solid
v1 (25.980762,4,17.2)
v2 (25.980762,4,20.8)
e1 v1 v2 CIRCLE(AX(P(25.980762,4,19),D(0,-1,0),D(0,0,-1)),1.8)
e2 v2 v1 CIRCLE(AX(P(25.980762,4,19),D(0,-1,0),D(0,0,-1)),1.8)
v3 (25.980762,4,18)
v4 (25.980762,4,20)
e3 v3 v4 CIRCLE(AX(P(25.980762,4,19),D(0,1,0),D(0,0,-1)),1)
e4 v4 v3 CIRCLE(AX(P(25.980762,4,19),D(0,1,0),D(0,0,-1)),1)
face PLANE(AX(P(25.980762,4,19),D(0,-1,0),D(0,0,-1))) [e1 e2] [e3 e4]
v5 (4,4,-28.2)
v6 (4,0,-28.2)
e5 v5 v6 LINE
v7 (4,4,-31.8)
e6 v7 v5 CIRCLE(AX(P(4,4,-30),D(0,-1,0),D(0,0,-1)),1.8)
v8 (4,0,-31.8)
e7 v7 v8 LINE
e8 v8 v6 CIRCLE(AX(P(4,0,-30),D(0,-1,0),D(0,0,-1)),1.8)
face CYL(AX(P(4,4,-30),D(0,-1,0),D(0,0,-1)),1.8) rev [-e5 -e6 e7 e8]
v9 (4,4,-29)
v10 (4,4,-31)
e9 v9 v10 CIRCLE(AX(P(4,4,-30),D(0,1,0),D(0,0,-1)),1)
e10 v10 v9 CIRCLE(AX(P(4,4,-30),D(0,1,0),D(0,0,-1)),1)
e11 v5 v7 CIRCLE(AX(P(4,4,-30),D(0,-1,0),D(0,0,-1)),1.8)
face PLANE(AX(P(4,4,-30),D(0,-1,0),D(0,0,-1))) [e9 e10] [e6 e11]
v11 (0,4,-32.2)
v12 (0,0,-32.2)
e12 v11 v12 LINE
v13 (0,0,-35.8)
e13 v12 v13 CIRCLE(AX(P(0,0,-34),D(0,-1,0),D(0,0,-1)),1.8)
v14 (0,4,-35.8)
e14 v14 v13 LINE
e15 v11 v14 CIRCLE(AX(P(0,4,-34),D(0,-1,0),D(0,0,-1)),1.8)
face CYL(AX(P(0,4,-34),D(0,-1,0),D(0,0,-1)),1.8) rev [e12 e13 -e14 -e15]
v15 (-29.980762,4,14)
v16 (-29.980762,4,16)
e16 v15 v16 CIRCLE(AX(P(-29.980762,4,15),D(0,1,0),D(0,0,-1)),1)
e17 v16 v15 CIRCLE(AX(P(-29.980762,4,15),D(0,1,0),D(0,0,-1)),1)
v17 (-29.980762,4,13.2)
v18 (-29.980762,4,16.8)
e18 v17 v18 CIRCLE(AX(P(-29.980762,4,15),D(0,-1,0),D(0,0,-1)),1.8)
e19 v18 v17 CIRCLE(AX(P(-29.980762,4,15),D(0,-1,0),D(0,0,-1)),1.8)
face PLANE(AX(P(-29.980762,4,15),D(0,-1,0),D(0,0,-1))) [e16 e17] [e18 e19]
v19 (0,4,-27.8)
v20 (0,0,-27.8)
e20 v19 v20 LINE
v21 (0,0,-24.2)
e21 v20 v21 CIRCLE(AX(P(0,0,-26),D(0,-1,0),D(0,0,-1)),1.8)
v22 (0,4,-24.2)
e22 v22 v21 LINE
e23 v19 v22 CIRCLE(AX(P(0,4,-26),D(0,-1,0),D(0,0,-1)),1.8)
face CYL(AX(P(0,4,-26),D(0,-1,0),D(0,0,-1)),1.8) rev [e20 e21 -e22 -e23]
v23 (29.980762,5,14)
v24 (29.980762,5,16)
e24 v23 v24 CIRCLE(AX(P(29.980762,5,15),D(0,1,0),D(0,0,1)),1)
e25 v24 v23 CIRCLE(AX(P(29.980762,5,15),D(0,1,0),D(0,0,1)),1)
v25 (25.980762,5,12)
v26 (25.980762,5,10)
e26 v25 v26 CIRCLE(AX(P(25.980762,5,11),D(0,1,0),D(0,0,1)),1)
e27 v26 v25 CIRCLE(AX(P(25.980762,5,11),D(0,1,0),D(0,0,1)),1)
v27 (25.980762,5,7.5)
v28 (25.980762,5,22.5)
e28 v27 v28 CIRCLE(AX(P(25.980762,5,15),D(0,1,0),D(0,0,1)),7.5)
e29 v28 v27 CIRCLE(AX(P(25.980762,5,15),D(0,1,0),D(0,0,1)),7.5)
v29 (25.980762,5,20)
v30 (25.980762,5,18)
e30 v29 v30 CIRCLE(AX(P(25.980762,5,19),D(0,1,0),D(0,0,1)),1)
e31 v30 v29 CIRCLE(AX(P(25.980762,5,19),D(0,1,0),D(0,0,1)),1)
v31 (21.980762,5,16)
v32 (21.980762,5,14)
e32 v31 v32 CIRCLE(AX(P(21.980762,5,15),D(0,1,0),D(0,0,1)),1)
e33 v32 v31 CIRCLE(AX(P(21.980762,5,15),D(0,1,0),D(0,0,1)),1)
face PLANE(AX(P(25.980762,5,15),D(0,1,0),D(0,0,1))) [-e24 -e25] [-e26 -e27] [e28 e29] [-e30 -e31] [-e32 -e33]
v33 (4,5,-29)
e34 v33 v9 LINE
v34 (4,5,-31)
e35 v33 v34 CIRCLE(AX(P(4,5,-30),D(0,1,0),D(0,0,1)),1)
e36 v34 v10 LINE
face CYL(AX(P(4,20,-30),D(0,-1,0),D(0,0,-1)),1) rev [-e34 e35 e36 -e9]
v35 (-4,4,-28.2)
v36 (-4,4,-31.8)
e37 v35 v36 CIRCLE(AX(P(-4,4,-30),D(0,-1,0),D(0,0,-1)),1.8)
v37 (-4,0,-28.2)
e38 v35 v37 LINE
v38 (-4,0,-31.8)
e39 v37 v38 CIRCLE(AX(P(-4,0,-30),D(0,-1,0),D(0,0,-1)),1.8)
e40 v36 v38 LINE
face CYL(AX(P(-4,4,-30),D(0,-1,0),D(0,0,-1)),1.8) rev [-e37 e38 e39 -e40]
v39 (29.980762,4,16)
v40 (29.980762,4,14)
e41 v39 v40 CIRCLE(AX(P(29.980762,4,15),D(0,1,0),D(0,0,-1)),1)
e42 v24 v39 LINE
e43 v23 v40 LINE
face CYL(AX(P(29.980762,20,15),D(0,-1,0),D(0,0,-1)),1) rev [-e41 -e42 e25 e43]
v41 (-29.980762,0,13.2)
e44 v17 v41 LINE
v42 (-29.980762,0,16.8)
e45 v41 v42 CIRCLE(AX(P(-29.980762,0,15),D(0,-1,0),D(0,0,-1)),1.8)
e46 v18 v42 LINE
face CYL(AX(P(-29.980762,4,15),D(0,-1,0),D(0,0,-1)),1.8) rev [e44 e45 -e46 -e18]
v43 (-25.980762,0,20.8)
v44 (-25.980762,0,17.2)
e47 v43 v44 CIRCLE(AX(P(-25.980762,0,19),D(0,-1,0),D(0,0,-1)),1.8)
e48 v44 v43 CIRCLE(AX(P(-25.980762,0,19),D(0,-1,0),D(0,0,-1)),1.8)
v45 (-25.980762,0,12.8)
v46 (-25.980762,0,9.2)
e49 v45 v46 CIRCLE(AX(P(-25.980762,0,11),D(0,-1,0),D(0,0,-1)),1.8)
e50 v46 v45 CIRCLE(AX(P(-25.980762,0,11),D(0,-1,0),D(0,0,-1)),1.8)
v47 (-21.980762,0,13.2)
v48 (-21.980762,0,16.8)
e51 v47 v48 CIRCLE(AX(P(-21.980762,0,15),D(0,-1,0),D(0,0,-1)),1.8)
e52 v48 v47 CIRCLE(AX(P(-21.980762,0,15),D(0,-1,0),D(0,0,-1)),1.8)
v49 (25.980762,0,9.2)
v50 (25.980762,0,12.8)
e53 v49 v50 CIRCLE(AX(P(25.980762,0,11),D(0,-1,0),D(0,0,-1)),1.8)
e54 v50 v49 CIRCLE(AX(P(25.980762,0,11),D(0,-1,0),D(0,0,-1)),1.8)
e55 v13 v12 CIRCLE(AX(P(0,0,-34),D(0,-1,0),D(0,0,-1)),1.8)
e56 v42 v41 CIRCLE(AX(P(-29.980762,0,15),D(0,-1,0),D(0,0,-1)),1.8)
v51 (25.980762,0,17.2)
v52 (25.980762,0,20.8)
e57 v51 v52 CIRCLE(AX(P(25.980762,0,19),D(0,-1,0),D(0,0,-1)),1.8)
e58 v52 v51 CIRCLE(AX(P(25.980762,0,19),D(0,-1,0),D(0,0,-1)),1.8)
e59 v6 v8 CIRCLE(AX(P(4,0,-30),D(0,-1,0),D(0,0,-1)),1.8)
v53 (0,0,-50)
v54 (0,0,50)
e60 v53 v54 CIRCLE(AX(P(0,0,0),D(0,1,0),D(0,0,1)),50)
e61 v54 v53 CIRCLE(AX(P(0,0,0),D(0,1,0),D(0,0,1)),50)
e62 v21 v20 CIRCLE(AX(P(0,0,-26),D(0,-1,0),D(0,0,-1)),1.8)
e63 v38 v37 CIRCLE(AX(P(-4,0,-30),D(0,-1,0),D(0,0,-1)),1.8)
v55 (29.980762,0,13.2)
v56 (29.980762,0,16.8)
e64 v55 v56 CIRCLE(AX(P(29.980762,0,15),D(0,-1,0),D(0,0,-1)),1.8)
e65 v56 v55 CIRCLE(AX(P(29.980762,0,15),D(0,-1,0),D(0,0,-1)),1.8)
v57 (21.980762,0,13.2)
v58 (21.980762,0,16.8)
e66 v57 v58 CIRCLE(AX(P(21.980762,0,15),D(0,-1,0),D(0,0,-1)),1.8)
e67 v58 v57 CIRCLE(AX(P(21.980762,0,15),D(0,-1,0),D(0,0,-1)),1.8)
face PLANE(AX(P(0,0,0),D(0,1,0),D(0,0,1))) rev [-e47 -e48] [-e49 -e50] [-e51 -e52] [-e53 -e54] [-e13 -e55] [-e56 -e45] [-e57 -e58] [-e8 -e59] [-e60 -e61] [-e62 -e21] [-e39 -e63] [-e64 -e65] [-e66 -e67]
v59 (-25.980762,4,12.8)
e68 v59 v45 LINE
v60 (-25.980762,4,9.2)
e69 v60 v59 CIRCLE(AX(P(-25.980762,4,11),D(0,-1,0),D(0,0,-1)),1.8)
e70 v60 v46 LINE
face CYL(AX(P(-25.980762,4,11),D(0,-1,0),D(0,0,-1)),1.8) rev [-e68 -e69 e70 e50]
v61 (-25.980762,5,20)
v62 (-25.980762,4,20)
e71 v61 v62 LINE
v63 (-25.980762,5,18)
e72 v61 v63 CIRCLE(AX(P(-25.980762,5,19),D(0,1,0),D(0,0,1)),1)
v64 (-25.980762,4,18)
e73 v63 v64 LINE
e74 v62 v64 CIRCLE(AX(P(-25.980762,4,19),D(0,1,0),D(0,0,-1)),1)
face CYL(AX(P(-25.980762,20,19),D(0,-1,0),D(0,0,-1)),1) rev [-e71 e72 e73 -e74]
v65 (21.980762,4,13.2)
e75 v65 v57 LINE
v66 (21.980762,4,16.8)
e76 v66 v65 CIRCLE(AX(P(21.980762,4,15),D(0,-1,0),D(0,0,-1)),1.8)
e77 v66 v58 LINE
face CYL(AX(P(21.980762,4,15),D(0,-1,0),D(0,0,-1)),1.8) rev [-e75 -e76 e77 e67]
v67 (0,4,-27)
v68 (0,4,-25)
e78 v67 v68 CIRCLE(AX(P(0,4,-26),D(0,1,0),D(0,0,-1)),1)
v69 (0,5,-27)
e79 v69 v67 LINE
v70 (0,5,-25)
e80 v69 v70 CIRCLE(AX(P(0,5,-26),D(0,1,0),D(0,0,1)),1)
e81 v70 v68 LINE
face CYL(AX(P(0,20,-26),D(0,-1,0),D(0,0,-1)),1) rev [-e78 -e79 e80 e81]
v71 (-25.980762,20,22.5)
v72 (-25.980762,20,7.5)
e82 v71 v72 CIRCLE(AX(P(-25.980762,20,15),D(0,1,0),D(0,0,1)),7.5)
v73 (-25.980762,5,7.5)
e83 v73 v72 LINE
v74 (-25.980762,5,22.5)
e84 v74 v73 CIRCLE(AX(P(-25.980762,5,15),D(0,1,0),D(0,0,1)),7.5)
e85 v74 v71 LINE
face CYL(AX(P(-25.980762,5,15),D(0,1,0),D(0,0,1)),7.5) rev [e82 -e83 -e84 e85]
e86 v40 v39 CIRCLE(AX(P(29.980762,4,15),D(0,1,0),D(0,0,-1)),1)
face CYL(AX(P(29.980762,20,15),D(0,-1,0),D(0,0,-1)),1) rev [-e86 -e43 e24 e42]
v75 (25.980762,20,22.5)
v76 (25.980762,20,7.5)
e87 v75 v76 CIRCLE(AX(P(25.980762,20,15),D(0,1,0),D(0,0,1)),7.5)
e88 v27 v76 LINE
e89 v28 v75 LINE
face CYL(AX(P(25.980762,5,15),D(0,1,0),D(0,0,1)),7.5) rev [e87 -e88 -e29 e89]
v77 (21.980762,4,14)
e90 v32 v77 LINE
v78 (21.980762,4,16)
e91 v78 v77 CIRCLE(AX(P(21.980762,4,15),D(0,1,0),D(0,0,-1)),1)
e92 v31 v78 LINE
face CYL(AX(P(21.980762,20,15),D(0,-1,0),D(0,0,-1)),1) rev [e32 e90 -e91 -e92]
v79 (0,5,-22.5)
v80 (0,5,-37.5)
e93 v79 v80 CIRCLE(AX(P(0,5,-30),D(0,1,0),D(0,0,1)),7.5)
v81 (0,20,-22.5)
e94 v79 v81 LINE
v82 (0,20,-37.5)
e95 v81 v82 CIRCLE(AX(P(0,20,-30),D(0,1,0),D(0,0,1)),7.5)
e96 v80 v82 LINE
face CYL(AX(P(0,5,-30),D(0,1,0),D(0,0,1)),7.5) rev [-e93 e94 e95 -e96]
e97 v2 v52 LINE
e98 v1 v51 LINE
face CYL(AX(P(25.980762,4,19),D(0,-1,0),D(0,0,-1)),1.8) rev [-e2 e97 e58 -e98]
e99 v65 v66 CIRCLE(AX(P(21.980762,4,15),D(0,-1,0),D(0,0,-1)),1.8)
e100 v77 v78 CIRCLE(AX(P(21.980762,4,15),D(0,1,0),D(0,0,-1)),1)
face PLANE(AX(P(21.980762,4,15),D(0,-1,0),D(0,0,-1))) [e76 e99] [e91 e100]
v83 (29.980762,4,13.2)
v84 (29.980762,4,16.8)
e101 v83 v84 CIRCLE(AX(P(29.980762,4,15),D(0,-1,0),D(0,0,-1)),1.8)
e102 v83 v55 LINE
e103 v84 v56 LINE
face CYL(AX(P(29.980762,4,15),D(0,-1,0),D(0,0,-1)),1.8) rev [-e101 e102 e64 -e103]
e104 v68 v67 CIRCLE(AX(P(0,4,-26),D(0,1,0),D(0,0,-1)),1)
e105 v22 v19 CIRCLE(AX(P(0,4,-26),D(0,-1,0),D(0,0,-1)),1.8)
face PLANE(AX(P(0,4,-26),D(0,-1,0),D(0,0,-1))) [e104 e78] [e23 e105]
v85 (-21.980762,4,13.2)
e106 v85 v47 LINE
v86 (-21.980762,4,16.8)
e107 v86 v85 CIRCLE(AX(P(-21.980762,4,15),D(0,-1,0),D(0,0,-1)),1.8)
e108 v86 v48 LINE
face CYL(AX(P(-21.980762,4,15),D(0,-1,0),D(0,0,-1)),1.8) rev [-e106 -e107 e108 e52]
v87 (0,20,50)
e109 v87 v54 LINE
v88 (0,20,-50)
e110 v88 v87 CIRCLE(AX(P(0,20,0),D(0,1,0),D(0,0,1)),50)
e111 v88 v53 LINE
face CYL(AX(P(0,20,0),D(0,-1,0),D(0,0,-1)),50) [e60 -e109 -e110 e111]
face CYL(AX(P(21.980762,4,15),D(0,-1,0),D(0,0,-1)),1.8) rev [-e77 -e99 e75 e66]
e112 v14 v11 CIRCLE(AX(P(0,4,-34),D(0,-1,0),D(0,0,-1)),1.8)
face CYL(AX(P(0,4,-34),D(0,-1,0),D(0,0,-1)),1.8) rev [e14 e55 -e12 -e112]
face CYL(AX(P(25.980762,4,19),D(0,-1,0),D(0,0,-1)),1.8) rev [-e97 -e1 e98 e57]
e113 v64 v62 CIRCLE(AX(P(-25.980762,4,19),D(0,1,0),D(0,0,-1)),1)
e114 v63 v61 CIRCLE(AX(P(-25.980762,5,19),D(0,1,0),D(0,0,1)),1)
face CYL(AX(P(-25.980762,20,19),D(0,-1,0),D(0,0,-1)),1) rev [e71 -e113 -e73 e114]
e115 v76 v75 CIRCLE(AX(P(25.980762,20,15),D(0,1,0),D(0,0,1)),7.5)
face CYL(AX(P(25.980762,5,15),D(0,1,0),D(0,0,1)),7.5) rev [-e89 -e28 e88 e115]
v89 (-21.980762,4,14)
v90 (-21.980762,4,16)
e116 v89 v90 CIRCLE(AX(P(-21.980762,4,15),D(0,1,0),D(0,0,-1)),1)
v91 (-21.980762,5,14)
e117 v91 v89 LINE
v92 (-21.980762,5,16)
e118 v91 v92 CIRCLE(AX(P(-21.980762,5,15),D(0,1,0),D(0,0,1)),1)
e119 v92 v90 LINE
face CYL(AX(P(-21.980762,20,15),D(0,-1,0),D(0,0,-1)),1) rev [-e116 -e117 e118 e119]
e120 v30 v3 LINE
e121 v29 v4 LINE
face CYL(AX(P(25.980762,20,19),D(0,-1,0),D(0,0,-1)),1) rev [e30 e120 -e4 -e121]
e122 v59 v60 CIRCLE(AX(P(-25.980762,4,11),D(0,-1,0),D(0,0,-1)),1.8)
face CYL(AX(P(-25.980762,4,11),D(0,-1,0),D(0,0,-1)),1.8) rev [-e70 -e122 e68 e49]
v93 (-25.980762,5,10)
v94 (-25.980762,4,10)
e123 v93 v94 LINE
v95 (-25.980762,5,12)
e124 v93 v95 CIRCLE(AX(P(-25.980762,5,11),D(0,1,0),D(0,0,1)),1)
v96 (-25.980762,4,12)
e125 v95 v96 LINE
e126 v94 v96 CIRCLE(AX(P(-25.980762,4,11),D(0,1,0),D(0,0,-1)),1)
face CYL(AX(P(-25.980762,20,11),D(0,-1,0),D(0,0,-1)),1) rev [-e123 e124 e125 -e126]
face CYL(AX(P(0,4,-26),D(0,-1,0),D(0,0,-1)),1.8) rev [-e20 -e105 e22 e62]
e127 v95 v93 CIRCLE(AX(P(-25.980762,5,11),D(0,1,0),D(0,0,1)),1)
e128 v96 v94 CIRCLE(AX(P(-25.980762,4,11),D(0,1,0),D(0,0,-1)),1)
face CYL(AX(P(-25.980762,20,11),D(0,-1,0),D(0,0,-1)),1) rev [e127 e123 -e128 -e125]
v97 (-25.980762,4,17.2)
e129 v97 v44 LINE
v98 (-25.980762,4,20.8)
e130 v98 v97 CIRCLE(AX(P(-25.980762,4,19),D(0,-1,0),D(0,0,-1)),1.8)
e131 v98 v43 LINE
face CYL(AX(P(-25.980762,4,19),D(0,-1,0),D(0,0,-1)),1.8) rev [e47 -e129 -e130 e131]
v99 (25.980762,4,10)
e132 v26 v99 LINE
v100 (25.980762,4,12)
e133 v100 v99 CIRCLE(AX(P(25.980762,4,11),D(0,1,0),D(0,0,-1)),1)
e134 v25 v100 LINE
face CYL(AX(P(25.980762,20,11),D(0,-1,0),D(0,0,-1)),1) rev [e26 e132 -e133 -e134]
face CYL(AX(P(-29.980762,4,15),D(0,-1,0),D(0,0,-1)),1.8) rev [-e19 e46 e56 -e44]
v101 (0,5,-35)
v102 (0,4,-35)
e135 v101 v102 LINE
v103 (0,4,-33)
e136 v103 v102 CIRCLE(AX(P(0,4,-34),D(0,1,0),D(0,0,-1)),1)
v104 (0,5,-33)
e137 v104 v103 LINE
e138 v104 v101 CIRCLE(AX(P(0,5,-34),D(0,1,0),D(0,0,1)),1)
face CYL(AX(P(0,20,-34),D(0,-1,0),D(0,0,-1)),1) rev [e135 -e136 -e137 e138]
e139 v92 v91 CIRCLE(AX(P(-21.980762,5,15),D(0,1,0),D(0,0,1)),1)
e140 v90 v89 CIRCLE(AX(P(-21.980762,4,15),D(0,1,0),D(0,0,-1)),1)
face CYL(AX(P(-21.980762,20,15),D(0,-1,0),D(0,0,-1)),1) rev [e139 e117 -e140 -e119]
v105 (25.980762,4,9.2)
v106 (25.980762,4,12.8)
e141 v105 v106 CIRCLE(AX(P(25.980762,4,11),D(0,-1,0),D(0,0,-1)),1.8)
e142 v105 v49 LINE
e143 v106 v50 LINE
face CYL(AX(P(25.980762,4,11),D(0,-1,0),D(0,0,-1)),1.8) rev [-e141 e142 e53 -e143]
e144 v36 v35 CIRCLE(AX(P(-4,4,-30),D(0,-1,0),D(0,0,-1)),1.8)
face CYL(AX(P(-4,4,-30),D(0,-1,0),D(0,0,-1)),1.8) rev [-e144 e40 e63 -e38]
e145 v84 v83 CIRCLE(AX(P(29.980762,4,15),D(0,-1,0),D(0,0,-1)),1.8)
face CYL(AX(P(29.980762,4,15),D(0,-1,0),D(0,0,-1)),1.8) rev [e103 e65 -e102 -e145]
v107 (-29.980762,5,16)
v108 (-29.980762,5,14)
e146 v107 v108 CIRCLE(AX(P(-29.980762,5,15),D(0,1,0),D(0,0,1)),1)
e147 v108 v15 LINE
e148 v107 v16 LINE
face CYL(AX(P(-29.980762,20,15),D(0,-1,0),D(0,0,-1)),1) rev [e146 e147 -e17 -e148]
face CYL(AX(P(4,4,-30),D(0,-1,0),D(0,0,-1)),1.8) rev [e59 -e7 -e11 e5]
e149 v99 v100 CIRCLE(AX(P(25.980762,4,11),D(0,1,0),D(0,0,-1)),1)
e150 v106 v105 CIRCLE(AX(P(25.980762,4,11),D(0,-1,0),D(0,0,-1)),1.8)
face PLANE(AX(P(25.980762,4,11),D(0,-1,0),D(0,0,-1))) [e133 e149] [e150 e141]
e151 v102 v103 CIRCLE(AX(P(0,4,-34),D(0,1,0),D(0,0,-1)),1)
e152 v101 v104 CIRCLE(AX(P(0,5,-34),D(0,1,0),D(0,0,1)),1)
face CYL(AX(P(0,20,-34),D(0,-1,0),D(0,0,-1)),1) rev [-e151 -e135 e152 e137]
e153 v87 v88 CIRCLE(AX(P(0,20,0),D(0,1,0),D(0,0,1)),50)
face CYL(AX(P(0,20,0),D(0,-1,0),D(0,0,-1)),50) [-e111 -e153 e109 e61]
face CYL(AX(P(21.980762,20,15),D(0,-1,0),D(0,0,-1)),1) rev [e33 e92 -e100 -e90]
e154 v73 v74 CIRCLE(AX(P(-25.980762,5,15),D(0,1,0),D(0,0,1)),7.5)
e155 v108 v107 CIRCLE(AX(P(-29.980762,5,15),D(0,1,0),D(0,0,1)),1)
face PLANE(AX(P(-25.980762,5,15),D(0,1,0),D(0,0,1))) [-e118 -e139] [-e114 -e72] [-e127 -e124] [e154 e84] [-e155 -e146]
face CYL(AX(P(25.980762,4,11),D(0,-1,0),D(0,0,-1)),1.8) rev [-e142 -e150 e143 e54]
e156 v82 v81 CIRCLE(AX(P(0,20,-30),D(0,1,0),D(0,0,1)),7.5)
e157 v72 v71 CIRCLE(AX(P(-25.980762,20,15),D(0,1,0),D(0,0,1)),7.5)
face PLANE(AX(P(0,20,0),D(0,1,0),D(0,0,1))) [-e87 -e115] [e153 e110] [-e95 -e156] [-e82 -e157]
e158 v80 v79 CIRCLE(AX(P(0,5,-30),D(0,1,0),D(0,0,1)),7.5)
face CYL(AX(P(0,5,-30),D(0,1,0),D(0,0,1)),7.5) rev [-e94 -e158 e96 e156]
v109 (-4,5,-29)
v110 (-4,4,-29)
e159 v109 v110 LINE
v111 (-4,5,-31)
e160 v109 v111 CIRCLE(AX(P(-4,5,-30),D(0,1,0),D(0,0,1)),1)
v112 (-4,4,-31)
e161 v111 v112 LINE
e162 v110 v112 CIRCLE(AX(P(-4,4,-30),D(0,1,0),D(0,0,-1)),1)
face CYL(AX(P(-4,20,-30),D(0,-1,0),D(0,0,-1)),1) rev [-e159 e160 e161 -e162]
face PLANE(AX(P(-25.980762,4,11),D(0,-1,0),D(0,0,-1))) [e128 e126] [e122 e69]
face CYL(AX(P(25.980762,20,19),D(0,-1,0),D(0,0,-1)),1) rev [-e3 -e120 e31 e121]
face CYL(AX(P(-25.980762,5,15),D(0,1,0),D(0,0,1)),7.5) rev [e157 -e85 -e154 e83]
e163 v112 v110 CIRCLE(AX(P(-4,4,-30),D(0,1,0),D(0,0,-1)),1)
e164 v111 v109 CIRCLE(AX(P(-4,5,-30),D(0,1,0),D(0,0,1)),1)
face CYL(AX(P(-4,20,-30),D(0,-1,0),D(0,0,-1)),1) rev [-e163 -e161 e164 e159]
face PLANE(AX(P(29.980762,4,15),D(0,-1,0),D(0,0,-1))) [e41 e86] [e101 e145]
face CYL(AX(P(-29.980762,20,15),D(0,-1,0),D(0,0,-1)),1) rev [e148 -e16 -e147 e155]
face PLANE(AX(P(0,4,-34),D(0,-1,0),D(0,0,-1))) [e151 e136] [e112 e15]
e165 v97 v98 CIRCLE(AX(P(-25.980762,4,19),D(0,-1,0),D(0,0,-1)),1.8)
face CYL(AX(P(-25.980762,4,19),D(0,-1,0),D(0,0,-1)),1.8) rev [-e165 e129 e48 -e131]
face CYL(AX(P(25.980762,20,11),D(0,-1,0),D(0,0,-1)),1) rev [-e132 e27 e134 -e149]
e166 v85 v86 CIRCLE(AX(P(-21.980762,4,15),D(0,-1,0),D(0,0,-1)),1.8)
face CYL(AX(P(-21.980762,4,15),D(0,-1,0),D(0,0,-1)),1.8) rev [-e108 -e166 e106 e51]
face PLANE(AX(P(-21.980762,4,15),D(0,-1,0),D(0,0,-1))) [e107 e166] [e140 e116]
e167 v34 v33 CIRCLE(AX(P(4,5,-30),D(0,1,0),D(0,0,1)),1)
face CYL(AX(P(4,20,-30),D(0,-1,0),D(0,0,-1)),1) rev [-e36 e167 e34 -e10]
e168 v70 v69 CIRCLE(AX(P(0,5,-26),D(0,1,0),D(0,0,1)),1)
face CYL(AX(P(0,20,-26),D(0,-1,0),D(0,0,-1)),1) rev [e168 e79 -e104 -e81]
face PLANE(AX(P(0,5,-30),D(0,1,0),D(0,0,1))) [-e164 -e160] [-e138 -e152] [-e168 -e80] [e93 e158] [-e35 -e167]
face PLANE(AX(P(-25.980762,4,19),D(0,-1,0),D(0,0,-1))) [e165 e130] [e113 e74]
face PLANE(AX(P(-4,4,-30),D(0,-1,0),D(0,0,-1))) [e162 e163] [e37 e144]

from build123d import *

# Parameters (mm, degrees)
SKETCH1_R           = 50
BOSS_EXTRUDE1_DEPTH = 20
SKETCH2_R           = 7.5
CUT_EXTRUDE1_DEPTH  = 15
SKETCH3_R           = 1
CUT_EXTRUDE2_DEPTH  = 74.484692283
SKETCH4_R           = 1.8
CUT_EXTRUDE3_DEPTH  = 4


with BuildPart() as part:
    # Sketch1 → Boss-Extrude1 (new body)
    with BuildSketch(Plane(origin=(0, 0, 0), x_dir=(1, 0, 0), z_dir=(0, 1, 0))):
        with Locations(Location((0, 0, 0), (0, 0, 270))):
            Circle(SKETCH1_R)
    extrude(amount=BOSS_EXTRUDE1_DEPTH)

    # Sketch2 → Cut-Extrude1 (cut)
    with BuildSketch(Plane(origin=(0, 20, 0), x_dir=(1, 0, 0), z_dir=(0, 1, 0))):
        with Locations(Location((0, 30, 0), (0, 0, 270))):
            Circle(SKETCH2_R)
        with Locations(Location((25.980762114, -15, 0), (0, 0, 270))):
            Circle(SKETCH2_R)
        with Locations(Location((-25.980762114, -15, 0), (0, 0, 270))):
            Circle(SKETCH2_R)
    extrude(amount=-CUT_EXTRUDE1_DEPTH, mode=Mode.SUBTRACT)

    # Sketch3 → Cut-Extrude2 (cut, through all)
    with BuildSketch(Plane.XZ):
        with Locations(Location((25.980762114, 19, 0), (0, 0, 270))):
            Circle(SKETCH3_R)
        with Locations(Location((29.980762114, 15, 0), (0, 0, 270))):
            Circle(SKETCH3_R)
        with Locations(Location((21.980762114, 15, 0), (0, 0, 270))):
            Circle(SKETCH3_R)
        with Locations(Location((25.980762114, 11, 0), (0, 0, 270))):
            Circle(SKETCH3_R)
        with Locations(Location((-25.980762114, 19, 0), (0, 0, 270))):
            Circle(SKETCH3_R)
        with Locations(Location((-29.980762114, 15, 0), (0, 0, 270))):
            Circle(SKETCH3_R)
        with Locations(Location((-25.980762114, 11, 0), (0, 0, 270))):
            Circle(SKETCH3_R)
        with Locations(Location((-21.980762114, 15, 0), (0, 0, 270))):
            Circle(SKETCH3_R)
        with Locations(Location((0, -26, 0), (0, 0, 270))):
            Circle(SKETCH3_R)
        with Locations(Location((-4, -30, 0), (0, 0, 270))):
            Circle(SKETCH3_R)
        with Locations(Location((0, -34, 0), (0, 0, 270))):
            Circle(SKETCH3_R)
        with Locations(Location((4, -30, 0), (0, 0, 270))):
            Circle(SKETCH3_R)
    extrude(amount=-CUT_EXTRUDE2_DEPTH, mode=Mode.SUBTRACT)

    # Sketch4 → Cut-Extrude3 (cut)
    with BuildSketch(Plane.XZ):
        with Locations(Location((-25.980762114, 19, 0), (0, 0, 270))):
            Circle(SKETCH4_R)
        with Locations(Location((-29.980762114, 15, 0), (0, 0, 270))):
            Circle(SKETCH4_R)
        with Locations(Location((-25.980762114, 11, 0), (0, 0, 270))):
            Circle(SKETCH4_R)
        with Locations(Location((-21.980762114, 15, 0), (0, 0, 270))):
            Circle(SKETCH4_R)
        with Locations(Location((25.980762114, 19, 0), (0, 0, 270))):
            Circle(SKETCH4_R)
        with Locations(Location((21.980762114, 15, 0), (0, 0, 270))):
            Circle(SKETCH4_R)
        with Locations(Location((25.980762114, 11, 0), (0, 0, 270))):
            Circle(SKETCH4_R)
        with Locations(Location((29.980762114, 15, 0), (0, 0, 270))):
            Circle(SKETCH4_R)
        with Locations(Location((0, -26, 0), (0, 0, 270))):
            Circle(SKETCH4_R)
        with Locations(Location((-4, -30, 0), (0, 0, 270))):
            Circle(SKETCH4_R)
        with Locations(Location((0, -34, 0), (0, 0, 270))):
            Circle(SKETCH4_R)
        with Locations(Location((4, -30, 0), (0, 0, 270))):
            Circle(SKETCH4_R)
    extrude(amount=-CUT_EXTRUDE3_DEPTH, mode=Mode.SUBTRACT)


solid = part.part
